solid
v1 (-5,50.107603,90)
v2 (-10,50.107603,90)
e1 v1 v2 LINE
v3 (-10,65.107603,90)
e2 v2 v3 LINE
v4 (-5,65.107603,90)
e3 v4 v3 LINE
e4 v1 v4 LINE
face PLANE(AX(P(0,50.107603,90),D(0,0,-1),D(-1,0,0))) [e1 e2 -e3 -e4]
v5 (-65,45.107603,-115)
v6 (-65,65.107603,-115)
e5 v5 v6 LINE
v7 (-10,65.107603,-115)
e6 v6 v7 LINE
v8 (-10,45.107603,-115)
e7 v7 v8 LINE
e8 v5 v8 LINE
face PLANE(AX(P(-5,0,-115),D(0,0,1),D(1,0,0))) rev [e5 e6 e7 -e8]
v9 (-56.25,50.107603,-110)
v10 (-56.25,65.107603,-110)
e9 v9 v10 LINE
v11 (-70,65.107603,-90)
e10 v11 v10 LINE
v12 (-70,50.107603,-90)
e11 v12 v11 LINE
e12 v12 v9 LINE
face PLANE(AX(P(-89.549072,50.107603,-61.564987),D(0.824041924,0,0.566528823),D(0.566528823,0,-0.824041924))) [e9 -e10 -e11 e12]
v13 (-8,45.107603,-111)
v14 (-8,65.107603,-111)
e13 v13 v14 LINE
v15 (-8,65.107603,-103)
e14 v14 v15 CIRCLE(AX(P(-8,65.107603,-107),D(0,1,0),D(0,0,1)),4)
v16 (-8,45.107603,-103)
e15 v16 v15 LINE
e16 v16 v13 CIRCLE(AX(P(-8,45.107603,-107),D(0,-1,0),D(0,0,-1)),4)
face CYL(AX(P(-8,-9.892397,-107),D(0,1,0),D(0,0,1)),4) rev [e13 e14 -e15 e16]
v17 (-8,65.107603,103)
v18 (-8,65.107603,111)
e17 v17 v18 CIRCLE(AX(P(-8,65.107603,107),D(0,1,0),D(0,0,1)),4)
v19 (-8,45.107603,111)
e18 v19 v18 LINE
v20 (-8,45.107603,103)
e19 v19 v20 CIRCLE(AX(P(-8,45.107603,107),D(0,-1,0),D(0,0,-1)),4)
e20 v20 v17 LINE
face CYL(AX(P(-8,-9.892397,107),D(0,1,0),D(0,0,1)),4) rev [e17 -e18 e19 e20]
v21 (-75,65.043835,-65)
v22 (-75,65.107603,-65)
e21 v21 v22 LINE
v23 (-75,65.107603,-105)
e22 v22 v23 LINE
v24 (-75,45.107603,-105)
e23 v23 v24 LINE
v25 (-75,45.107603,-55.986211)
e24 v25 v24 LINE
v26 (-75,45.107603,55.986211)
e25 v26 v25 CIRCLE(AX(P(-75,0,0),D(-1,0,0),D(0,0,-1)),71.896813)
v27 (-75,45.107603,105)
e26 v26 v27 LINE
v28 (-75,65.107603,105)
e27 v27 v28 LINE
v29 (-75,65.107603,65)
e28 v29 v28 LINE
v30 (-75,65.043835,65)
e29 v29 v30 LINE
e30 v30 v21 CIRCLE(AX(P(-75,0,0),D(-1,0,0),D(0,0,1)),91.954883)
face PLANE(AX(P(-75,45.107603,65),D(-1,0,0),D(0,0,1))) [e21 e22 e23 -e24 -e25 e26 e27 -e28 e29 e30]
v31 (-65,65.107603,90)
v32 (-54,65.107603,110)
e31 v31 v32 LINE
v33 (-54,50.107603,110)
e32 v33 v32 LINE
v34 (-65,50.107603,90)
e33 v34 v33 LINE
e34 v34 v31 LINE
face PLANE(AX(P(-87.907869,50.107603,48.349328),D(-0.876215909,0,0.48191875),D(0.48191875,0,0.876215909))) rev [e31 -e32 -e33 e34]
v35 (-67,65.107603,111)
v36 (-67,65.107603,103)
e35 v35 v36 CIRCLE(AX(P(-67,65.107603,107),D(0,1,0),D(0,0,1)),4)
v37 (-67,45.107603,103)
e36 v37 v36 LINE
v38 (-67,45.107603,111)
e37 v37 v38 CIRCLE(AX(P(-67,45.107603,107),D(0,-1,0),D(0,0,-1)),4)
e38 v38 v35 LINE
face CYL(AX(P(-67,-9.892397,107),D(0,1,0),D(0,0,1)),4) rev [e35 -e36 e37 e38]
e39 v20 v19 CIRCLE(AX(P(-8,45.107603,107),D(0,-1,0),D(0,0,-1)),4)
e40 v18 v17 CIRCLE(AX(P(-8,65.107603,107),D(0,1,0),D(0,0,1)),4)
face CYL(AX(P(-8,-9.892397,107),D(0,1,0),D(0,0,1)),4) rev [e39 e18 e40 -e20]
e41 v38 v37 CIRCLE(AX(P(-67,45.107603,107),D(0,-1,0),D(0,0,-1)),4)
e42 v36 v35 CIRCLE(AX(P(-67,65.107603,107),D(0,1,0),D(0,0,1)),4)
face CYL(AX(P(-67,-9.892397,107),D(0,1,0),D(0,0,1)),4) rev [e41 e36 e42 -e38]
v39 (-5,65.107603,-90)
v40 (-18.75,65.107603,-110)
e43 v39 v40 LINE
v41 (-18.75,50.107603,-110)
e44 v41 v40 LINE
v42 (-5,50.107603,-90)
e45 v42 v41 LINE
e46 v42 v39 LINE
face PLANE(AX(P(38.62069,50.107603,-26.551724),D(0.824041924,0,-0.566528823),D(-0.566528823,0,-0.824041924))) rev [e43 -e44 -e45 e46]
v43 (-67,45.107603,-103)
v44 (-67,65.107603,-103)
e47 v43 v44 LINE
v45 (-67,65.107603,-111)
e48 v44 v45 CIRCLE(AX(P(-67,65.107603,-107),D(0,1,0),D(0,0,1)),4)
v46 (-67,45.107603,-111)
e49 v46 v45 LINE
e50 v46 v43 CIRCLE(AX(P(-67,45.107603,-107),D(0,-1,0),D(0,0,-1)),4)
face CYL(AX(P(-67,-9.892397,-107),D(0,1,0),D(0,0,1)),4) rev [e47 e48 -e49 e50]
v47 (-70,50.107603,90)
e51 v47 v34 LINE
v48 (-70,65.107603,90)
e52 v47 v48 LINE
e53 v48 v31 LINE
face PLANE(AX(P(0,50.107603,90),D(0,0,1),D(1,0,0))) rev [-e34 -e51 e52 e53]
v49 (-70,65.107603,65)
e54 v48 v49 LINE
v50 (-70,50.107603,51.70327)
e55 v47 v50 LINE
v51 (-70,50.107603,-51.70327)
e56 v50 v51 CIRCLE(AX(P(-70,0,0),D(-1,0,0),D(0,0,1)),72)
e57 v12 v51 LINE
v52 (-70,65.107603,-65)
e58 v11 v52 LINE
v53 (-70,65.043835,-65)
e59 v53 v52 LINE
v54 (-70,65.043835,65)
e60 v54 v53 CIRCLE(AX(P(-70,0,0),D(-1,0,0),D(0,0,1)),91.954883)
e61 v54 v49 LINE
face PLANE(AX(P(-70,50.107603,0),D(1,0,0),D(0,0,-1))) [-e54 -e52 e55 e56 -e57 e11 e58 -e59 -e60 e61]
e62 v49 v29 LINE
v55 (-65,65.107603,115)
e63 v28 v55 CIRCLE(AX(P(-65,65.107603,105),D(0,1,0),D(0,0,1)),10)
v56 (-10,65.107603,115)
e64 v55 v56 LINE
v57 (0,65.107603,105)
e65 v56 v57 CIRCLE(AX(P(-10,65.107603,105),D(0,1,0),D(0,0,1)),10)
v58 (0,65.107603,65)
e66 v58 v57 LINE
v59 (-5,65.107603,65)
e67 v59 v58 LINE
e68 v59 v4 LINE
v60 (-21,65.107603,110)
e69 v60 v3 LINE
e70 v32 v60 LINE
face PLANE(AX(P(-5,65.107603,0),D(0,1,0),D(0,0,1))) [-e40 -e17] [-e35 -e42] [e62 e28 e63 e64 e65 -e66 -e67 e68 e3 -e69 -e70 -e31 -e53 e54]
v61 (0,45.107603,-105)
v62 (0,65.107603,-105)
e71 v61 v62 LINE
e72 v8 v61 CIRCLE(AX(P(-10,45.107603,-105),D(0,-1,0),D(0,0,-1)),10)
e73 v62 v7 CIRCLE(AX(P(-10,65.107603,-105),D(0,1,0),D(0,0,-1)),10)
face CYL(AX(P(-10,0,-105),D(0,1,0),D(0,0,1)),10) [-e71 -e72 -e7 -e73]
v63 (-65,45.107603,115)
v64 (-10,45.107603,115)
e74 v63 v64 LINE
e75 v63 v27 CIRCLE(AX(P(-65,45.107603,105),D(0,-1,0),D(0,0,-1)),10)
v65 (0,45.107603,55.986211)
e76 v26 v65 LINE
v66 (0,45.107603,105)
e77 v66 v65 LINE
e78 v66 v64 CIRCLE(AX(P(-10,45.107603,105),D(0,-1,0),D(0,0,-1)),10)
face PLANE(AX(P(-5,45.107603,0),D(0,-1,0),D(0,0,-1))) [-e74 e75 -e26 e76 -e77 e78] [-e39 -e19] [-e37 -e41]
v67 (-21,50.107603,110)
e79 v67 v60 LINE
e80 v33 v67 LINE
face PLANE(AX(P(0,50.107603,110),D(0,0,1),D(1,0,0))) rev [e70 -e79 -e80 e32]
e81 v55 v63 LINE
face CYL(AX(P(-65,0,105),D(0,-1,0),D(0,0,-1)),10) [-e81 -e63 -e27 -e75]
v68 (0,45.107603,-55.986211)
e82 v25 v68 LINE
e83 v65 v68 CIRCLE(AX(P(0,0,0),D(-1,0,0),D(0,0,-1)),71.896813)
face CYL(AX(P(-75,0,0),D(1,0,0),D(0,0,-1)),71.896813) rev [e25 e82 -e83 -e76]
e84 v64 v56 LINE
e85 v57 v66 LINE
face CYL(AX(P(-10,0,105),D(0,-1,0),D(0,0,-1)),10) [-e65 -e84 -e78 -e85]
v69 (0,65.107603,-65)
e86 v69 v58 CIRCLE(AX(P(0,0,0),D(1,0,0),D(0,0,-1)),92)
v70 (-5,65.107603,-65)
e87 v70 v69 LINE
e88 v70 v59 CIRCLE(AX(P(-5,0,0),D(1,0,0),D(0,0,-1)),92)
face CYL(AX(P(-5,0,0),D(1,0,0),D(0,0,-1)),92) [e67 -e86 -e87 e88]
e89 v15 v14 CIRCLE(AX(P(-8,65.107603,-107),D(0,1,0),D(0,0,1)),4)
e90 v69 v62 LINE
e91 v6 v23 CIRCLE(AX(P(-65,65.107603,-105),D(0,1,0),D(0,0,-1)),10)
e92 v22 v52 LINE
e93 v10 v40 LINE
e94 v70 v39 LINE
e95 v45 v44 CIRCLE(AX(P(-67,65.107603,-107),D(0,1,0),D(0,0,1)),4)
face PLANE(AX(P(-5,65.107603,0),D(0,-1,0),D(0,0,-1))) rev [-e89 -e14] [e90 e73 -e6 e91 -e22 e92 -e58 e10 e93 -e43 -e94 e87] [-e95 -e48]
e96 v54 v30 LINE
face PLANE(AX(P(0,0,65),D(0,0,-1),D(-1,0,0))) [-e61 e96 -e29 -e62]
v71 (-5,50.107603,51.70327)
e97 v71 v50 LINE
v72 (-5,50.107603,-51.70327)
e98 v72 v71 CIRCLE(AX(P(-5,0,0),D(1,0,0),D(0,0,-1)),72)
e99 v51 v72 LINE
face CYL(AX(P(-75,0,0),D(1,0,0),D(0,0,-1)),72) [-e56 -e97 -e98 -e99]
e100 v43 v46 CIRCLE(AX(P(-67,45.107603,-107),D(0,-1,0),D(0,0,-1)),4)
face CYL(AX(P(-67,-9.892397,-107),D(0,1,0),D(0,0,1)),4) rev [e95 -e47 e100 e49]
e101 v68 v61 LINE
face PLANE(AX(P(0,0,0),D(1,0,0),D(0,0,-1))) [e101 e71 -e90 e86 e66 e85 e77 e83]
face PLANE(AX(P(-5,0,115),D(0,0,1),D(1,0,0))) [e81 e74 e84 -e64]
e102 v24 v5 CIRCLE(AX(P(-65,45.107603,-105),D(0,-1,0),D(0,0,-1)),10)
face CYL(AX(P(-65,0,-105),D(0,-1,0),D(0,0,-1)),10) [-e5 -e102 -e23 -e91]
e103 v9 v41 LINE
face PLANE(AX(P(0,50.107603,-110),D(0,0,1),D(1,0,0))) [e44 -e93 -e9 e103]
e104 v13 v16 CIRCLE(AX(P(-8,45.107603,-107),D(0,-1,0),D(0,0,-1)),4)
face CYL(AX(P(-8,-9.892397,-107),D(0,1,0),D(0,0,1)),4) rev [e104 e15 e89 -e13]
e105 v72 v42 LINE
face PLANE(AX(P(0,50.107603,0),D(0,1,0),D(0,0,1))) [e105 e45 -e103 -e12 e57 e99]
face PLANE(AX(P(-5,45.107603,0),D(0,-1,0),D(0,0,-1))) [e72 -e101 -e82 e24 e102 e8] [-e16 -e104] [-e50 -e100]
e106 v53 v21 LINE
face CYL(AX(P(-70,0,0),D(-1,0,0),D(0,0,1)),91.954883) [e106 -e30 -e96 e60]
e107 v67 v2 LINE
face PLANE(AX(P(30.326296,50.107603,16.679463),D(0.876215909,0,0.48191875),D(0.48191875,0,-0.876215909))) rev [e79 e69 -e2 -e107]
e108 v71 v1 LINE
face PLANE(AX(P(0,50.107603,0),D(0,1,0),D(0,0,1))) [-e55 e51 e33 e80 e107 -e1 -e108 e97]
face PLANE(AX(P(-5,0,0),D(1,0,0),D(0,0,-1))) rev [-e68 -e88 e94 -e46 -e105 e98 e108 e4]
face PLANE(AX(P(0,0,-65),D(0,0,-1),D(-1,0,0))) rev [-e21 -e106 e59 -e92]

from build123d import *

# Parameters (mm, degrees)
SIDE_WALL_DEPTH           = 5
END_FLANGE_A_DEPTH        = 50
FLANGE_A_POCKET_DEPTH     = 15
ARCH_SHELL_DEPTH          = 75
SIDE_START                = -5
SIDE_WALL_EXTENSION_DEPTH = 5
FLANGE_START              = -75
FLANGE_A_RIM_DEPTH        = 75
END_FLANGE_B_SKETCH_W     = 75
END_FLANGE_B_SKETCH_H     = 20
END_FLANGE_B_DEPTH        = 50
FLANGE_B_POCKET_DEPTH     = 15
FLANGE_B_RIM_DEPTH        = 75
BOLT_HOLES_SKETCH_R       = 4
BOLT_HOLES_4X_DEPTH       = 75
CORNER_FILLETS_R10_A_R    = 10
CORNER_FILLETS_R10_B_R    = 10
CORNER_FILLETS_R10_C_R    = 10
CORNER_FILLETS_R10_D_R    = 10


with BuildPart() as part:
    # Side Wall Profile Sketch → Side Wall (new body)
    with BuildSketch(Plane(origin=(0, 0, 0), x_dir=(0, 0, -1), z_dir=(1, 0, 0))):
        with BuildLine():
            ThreePointArc((56.118661154, 45.107603243), (0, 72), (-56.118661154, 45.107603243))
            Line((-56.118661154, 45.107603243), (-115, 45.107603243))
            Line((-115, 45.107603243), (-115, 65.107603243))
            Line((-115, 65.107603243), (-65, 65.107603243))
            ThreePointArc((-65, 65.107603243), (0, 92), (65, 65.107603243))
            Line((65, 65.107603243), (115, 65.107603243))
            Line((115, 65.107603243), (115, 45.107603243))
            Line((115, 45.107603243), (95, 45.107603243))
            Line((95, 45.107603243), (56.118661154, 45.107603243))
        make_face()
    extrude(amount=-SIDE_WALL_DEPTH)

    # End Flange A Sketch → End Flange A (add)
    with BuildSketch(Plane.XY.offset(115)):
        Polygon((0, 45.107603243), (-75, 45.107603243), (-75, 65.107603243), (-5, 65.107603243), (0, 65.107603243), align=None)
    extrude(amount=-END_FLANGE_A_DEPTH)

    # Flange A Pocket Sketch → Flange A Pocket (cut)
    with BuildSketch(Plane(origin=(0, 65.107603243, 0), x_dir=(1, 0, 0), z_dir=(0, 1, 0))):
        Polygon((-10, -90), (-5, -90), (-5, -65), (-70, -65), (-70, -90), (-65, -90), (-54, -110), (-21, -110), align=None)
    extrude(amount=-FLANGE_A_POCKET_DEPTH, mode=Mode.SUBTRACT)

    # Arch Shell Sketch → Arch Shell (add)
    with BuildSketch(Plane(origin=(0, 0, 0), x_dir=(0, 0, -1), z_dir=(1, 0, 0))):
        with BuildLine():
            Line((-56.118661154, 45.107603243), (-55.986211495, 45.107603243))
            ThreePointArc((-55.986211495, 45.107603243), (0, 71.896813197), (55.986211495, 45.107603243))
            Line((55.986211495, 45.107603243), (56.118661154, 45.107603243))
            ThreePointArc((56.118661154, 45.107603243), (0, 72), (-56.118661154, 45.107603243))
        make_face()
    extrude(amount=-ARCH_SHELL_DEPTH)

    # Side Wall Extension Sketch → Side Wall Extension (add)
    with BuildSketch(Plane.ZY.offset(75).offset(SIDE_START)):
        with BuildLine():
            ThreePointArc((-65, 65.043834782), (-73.247030889, 55.592921393), (-80.131171043, 45.107603243))
            Line((-80.131171043, 45.107603243), (-65, 45.107603243))
            Line((-65, 45.107603243), (-56.118661154, 45.107603243))
            ThreePointArc((-56.118661154, 45.107603243), (0, 72), (56.118661154, 45.107603243))
            Line((56.118661154, 45.107603243), (65, 45.107603243))
            Line((65, 45.107603243), (65, 65.043834782))
            ThreePointArc((65, 65.043834782), (0, 91.95488265), (-65, 65.043834782))
        make_face()
    extrude(amount=SIDE_WALL_EXTENSION_DEPTH)

    # Flange A Rim Sketch → Flange A Rim (add)
    with BuildSketch(Plane.ZY.offset(75).offset(FLANGE_START)):
        with BuildLine():
            Line((55.986211495, 45.107603243), (65, 45.107603243))
            Line((65, 45.107603243), (65, 50.107603243))
            Line((65, 50.107603243), (51.559478713, 50.107603243))
            ThreePointArc((51.559478713, 50.107603243), (53.830928569, 47.659027238), (55.986211495, 45.107603243))
        make_face()
    extrude(amount=FLANGE_A_RIM_DEPTH)

    # End Flange B Sketch → End Flange B (add)
    with BuildSketch(Plane(origin=(0, 0, -115), x_dir=(-1, 0, 0), z_dir=(0, 0, -1))):
        with Locations((37.5, 55.107603243)):
            Rectangle(END_FLANGE_B_SKETCH_W, END_FLANGE_B_SKETCH_H)
    extrude(amount=-END_FLANGE_B_DEPTH)

    # Flange B Pocket Sketch → Flange B Pocket (cut)
    with BuildSketch(Plane(origin=(0, 65.107603243, 0), x_dir=(1, 0, 0), z_dir=(0, 1, 0))):
        Polygon((-56.25, 110), (-70, 90), (-70, 65), (-5, 65), (-5, 90), (-18.75, 110), (-37.5, 110), align=None)
    extrude(amount=-FLANGE_B_POCKET_DEPTH, mode=Mode.SUBTRACT)

    # Flange B Rim Sketch → Flange B Rim (add)
    with BuildSketch(Plane(origin=(0, 0, 0), x_dir=(0, 0, -1), z_dir=(1, 0, 0))):
        with BuildLine():
            Line((65, 45.107603243), (65, 50.107603243))
            Line((65, 50.107603243), (51.559478713, 50.107603243))
            ThreePointArc((51.559478713, 50.107603243), (53.830928569, 47.659027238), (55.986211495, 45.107603243))
            Line((55.986211495, 45.107603243), (65, 45.107603243))
        make_face()
    extrude(amount=-FLANGE_B_RIM_DEPTH)

    # Bolt Holes Sketch → Bolt Holes 4x (cut)
    with BuildSketch(Plane(origin=(0, 65.107603243, 0), x_dir=(1, 0, 0), z_dir=(0, 1, 0))):
        with Locations(Location((-8, 107, 0), (0, 0, 270))):
            Circle(BOLT_HOLES_SKETCH_R)
        with Locations(Location((-67, 107, 0), (0, 0, 270))):
            Circle(BOLT_HOLES_SKETCH_R)
        with Locations(Location((-8, -107, 0), (0, 0, 270))):
            Circle(BOLT_HOLES_SKETCH_R)
        with Locations(Location((-67, -107, 0), (0, 0, 270))):
            Circle(BOLT_HOLES_SKETCH_R)
    extrude(amount=-BOLT_HOLES_4X_DEPTH, mode=Mode.SUBTRACT)

    # Corner Fillets R10 A
    corner_fillets_r10_a_edges = [part.edges().sort_by_distance(p)[0] for p in [
        (0, 55.107603243, 115),
    ]]
    fillet(corner_fillets_r10_a_edges, radius=CORNER_FILLETS_R10_A_R)

    # Corner Fillets R10 B
    corner_fillets_r10_b_edges = [part.edges().sort_by_distance(p)[0] for p in [
        (-75, 55.107603243, 115),
    ]]
    fillet(corner_fillets_r10_b_edges, radius=CORNER_FILLETS_R10_B_R)

    # Corner Fillets R10 C
    corner_fillets_r10_c_edges = [part.edges().sort_by_distance(p)[0] for p in [
        (-75, 55.107603243, -115),
    ]]
    fillet(corner_fillets_r10_c_edges, radius=CORNER_FILLETS_R10_C_R)

    # Corner Fillets R10 D
    corner_fillets_r10_d_edges = [part.edges().sort_by_distance(p)[0] for p in [
        (0, 55.107603243, -115),
    ]]
    fillet(corner_fillets_r10_d_edges, radius=CORNER_FILLETS_R10_D_R)


solid = part.part
